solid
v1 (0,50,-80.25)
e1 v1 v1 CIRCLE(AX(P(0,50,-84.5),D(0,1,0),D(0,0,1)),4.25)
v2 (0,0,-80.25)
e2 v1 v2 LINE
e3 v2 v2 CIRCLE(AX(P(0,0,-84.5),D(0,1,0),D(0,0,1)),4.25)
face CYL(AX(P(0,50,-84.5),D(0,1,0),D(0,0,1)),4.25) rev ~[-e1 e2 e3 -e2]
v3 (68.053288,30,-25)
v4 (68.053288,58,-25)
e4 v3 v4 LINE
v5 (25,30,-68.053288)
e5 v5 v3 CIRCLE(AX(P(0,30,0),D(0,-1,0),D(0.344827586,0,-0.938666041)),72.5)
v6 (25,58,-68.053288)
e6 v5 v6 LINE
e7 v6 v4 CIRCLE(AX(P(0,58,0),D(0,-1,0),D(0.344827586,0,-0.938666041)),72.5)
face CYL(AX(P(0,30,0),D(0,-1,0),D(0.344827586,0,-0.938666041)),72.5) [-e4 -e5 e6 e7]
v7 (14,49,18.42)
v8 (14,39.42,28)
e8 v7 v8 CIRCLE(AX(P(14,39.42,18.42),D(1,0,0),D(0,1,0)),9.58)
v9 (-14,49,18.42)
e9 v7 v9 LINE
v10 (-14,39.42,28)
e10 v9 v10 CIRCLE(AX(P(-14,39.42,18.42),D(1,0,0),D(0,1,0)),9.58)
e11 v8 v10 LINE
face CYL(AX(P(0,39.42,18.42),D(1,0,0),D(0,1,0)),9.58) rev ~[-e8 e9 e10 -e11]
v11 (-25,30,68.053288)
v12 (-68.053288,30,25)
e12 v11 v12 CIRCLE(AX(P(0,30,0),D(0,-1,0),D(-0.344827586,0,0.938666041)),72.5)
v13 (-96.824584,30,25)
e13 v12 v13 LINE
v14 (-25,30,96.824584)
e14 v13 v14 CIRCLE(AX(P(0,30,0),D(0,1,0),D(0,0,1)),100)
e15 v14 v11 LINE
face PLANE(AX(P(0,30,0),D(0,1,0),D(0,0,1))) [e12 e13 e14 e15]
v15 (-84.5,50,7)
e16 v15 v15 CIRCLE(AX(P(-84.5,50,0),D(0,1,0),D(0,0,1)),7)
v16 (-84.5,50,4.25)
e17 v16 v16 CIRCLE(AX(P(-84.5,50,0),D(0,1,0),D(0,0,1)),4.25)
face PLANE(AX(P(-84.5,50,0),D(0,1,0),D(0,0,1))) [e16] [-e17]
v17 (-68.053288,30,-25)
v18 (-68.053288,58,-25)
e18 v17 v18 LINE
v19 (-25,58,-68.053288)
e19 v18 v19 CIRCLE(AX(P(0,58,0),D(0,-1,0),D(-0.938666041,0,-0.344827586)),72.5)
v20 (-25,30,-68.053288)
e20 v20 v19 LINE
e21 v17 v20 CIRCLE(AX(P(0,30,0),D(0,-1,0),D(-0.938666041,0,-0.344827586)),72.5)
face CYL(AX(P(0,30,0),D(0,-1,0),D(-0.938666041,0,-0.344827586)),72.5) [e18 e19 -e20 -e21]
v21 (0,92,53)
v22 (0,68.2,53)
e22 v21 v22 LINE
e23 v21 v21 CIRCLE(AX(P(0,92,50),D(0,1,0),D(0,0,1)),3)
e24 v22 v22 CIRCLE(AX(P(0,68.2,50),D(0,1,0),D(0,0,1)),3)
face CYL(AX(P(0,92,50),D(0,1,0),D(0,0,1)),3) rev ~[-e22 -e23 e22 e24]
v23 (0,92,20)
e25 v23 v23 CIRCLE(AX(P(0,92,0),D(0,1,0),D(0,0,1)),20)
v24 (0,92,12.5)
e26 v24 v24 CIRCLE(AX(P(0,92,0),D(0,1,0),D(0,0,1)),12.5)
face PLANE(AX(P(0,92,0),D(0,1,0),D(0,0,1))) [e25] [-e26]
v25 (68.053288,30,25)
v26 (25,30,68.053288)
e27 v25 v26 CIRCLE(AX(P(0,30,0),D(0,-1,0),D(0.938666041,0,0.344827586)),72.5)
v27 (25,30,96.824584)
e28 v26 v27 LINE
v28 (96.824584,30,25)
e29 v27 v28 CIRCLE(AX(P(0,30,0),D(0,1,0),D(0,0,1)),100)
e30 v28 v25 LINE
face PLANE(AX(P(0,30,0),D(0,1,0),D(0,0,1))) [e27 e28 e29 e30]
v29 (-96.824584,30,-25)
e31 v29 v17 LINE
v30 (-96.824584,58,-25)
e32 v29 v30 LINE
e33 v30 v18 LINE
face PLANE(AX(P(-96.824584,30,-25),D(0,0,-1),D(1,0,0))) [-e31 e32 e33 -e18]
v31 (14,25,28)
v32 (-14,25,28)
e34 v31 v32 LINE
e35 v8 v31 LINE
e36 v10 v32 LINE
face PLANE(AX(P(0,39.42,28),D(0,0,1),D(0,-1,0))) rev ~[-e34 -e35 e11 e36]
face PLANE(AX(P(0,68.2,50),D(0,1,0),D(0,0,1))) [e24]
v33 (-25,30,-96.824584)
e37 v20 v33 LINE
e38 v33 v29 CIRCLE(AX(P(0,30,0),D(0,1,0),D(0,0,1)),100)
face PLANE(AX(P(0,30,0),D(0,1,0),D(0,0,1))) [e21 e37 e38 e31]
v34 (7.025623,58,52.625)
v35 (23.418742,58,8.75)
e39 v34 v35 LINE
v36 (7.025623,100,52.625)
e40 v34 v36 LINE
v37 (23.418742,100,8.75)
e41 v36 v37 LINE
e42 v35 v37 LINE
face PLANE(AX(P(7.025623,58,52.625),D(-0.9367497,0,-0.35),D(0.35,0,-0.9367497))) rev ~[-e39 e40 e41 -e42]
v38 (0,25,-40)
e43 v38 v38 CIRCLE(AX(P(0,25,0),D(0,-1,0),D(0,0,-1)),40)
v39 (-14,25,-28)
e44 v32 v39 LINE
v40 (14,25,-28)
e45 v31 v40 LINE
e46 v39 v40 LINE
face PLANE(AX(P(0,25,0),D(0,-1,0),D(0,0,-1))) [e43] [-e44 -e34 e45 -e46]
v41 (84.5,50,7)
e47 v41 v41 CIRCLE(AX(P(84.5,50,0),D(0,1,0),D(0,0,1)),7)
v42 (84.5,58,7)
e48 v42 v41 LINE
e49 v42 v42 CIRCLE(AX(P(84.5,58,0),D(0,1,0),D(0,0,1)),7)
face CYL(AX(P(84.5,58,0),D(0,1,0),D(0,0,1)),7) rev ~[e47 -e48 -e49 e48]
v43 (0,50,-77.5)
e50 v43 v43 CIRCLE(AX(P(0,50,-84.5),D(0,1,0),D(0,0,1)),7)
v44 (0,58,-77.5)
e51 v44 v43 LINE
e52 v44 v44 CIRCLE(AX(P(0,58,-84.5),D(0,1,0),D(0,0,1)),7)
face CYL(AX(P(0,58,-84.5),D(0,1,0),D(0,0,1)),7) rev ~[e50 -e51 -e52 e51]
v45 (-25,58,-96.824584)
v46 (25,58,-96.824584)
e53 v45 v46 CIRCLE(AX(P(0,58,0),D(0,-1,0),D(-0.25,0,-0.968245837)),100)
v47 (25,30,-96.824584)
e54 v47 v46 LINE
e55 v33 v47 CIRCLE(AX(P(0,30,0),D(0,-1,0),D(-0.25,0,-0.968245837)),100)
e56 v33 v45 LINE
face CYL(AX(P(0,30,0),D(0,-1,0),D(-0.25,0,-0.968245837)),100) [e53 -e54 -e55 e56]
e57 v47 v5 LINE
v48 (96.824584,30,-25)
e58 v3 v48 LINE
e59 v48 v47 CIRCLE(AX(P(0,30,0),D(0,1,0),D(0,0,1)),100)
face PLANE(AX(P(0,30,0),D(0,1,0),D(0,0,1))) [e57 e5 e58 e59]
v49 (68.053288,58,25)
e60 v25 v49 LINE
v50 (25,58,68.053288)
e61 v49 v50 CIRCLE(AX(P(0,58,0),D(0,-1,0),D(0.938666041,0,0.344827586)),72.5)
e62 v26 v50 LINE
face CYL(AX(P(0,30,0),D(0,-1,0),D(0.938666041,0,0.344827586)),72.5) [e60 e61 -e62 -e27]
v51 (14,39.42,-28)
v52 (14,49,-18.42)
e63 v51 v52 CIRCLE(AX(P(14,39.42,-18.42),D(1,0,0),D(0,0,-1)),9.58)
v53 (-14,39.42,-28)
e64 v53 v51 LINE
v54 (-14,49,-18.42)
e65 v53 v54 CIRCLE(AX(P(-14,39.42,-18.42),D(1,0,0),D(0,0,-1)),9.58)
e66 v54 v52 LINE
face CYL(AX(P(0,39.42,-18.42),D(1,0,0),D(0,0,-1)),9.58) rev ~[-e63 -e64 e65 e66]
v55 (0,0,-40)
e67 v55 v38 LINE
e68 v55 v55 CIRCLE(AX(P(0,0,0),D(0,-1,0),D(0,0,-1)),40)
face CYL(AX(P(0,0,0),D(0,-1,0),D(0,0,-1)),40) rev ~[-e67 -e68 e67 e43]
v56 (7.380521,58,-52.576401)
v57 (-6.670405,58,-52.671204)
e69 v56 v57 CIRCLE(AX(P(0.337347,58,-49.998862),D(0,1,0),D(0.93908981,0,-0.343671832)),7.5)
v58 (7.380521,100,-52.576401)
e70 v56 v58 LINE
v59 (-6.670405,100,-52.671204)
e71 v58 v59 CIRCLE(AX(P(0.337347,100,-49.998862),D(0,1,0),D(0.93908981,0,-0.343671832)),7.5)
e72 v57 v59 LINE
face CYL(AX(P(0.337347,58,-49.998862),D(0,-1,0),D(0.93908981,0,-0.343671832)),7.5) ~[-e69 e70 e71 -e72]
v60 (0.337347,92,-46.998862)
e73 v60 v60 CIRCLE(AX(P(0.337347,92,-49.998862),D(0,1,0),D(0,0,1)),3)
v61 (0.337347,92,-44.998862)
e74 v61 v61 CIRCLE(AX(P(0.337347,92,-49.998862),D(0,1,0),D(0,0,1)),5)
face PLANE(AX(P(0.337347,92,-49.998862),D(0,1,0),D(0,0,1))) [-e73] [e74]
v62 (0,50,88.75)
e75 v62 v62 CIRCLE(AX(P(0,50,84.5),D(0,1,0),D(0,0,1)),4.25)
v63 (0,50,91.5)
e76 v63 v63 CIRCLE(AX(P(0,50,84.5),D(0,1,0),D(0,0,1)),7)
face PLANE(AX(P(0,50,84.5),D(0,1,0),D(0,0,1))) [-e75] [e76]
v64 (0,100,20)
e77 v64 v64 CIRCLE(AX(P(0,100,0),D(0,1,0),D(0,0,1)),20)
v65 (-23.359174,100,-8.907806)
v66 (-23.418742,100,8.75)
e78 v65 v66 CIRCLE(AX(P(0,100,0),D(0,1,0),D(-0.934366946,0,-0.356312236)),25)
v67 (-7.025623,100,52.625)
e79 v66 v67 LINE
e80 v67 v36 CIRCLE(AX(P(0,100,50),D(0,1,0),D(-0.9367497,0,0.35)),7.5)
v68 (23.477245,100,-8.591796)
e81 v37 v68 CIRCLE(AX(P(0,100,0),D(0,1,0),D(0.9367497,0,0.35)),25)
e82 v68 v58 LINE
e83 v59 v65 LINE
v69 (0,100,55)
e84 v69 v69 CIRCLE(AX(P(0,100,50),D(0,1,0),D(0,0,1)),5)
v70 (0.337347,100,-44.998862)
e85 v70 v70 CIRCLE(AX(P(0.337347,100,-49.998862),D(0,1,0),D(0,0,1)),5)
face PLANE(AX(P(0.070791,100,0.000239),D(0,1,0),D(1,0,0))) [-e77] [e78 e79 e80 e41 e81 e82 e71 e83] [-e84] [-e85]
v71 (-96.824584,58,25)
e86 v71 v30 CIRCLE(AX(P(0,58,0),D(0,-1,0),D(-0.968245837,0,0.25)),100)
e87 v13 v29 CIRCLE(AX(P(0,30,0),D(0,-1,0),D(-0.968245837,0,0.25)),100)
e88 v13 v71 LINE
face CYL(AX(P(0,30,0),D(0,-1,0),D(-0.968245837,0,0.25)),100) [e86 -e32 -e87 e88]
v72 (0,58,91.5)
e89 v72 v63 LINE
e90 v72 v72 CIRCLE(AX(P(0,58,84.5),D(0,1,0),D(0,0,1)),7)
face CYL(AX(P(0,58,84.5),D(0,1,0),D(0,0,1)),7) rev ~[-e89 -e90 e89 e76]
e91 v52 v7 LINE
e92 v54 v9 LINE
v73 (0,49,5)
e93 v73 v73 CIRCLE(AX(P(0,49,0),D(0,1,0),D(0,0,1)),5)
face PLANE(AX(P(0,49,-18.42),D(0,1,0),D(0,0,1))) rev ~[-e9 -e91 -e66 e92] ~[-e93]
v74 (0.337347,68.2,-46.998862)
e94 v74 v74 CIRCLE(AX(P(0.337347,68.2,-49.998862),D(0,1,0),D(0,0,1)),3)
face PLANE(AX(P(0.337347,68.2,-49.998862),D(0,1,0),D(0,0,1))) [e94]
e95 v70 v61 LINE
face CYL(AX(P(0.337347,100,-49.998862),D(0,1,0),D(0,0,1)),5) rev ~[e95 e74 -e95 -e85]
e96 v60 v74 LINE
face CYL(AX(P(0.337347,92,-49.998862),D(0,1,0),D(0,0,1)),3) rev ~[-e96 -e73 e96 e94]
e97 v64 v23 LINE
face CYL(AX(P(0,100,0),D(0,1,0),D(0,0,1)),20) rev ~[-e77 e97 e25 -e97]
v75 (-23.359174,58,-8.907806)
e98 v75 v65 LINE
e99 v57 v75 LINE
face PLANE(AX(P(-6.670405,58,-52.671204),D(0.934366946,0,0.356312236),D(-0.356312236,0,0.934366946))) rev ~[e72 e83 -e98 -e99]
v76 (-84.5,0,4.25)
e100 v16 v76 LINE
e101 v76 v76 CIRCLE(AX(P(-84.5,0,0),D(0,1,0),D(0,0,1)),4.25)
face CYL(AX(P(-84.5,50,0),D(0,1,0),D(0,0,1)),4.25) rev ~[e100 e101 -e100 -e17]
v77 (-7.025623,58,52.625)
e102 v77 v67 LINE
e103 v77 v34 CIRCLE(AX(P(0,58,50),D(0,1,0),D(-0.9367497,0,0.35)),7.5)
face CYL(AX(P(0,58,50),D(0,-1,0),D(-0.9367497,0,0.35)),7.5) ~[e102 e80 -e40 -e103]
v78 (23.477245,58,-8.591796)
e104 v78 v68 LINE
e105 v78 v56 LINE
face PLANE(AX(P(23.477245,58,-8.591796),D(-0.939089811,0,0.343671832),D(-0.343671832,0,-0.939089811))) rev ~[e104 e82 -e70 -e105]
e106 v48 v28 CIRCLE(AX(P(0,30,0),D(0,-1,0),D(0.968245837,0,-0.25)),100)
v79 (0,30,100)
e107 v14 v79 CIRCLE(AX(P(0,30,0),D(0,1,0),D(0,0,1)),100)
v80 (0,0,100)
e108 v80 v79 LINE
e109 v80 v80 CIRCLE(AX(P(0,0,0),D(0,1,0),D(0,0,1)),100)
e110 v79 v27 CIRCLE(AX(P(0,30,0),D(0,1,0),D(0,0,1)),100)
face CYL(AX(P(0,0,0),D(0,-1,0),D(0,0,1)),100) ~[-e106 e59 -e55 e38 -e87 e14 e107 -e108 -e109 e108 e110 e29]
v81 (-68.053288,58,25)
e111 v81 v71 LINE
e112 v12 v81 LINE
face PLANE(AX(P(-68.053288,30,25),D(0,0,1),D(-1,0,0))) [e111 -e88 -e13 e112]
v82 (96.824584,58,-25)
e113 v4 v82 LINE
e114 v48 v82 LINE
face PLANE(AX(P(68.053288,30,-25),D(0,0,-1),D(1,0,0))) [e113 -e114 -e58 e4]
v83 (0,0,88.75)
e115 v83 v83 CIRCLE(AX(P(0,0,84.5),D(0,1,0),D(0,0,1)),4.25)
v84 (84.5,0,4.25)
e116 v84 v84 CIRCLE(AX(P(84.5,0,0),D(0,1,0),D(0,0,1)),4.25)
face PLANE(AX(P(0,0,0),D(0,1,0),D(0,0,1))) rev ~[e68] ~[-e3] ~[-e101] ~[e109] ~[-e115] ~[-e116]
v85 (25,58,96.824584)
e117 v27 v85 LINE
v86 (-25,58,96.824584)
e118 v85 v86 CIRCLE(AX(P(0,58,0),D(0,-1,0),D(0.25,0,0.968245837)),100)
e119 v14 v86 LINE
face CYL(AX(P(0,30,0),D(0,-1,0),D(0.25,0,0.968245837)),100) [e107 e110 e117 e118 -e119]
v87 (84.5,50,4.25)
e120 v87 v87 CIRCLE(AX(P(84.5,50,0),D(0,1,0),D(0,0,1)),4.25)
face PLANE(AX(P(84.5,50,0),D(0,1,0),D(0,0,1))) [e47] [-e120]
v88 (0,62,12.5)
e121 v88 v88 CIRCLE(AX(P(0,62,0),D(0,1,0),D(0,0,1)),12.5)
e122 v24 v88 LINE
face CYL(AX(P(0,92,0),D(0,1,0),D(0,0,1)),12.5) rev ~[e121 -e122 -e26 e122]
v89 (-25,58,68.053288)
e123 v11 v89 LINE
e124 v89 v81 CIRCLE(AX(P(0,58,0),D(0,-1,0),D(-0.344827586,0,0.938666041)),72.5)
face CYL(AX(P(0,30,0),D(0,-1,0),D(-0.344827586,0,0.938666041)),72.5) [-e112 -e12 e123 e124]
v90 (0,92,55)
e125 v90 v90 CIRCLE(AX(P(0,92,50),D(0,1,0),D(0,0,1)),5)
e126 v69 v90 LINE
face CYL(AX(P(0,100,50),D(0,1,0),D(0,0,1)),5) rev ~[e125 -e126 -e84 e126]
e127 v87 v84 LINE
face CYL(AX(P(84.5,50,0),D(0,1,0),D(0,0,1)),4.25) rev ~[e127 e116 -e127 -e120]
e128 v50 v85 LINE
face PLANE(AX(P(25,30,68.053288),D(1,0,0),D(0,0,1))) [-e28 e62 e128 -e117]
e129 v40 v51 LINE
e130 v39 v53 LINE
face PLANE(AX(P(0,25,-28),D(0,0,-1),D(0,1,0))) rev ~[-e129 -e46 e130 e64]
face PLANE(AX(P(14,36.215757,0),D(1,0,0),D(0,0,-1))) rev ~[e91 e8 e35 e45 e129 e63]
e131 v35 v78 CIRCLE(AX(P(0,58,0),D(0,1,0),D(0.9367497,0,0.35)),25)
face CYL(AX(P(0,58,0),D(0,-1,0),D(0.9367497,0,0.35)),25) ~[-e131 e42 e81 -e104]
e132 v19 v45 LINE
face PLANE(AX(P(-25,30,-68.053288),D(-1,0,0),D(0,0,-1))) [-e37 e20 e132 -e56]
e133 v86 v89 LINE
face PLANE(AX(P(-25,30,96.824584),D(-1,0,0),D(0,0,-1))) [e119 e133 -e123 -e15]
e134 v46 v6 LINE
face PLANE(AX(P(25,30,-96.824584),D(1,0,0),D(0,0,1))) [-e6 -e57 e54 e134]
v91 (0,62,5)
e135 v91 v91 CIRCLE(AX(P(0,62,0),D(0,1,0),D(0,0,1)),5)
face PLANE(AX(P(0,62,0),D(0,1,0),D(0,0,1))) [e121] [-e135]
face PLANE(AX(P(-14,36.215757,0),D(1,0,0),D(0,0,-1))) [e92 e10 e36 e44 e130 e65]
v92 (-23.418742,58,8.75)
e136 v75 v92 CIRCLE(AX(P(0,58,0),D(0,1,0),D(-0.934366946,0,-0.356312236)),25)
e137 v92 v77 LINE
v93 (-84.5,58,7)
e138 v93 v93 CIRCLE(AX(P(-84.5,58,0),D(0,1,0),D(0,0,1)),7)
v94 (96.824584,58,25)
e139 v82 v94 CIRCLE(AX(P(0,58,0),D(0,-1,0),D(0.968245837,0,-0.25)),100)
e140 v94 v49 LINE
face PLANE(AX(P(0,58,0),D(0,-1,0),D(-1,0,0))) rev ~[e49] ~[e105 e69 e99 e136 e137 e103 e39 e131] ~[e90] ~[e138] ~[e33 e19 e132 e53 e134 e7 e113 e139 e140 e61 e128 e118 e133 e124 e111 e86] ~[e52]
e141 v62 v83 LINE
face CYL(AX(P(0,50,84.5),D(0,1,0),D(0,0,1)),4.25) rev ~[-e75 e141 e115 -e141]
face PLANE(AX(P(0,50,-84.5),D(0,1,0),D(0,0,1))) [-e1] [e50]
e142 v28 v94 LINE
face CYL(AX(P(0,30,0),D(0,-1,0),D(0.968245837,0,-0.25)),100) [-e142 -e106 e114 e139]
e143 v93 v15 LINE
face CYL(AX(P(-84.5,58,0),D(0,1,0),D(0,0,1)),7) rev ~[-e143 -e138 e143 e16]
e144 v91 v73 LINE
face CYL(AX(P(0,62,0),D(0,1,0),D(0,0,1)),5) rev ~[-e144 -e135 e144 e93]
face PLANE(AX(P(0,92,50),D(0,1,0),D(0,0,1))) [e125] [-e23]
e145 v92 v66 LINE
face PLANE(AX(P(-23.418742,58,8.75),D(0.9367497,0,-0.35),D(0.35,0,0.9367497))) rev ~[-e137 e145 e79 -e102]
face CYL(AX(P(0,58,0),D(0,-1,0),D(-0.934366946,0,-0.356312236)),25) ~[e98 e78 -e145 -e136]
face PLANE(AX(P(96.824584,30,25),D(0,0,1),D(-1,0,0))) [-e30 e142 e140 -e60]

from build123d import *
from build123d.topology import SkipClean

# Parameters (mm, degrees)
BASE_FLANGE_SKETCH_R               = 100
BASE_FLANGE_200_DEPTH              = 30
MOUNTING_PAD_DEPTH                 = 28
MOUNTING_COUNTERBORES_SKETCH_R     = 7
MOUNTING_COUNTERBORES_4X_14_DEPTH  = 8
MOUNTING_HOLES_SKETCH_R            = 4.25
MOUNTING_HOLES_4X_8_5_DEPTH        = 50
SUPPORT_BOSS_DEPTH                 = 42
BEARING_COUNTERBORE_SKETCH_R       = 20
BEARING_COUNTERBORE_40_DEPTH       = 8
BEARING_BORE_SKETCH_R              = 12.5
BEARING_BORE_25_DEPTH              = 30
THROUGH_BORE_SKETCH_R              = 5
THROUGH_BORE_10_DEPTH              = 13
UNDERSIDE_RECESS_SKETCH_R          = 40
UNDERSIDE_RECESS_80_DEPTH          = 25
SIDE_SLOT_DEPTH                    = 14
BOSS_HOLE_COUNTERBORES_SKETCH_R    = 5
BOSS_HOLE_COUNTERBORES_2X_10_DEPTH = 8
BOSS_PIN_HOLES_SKETCH_R            = 3
BOSS_PIN_HOLES_2X_6_DEPTH          = 23.8


with BuildPart() as part:
    # Base Flange Sketch → Base Flange Ø200 (new body)
    with BuildSketch(Plane(origin=(0, 0, 0), x_dir=(1, 0, 0), z_dir=(0, 1, 0))):
        with Locations(Location((0, 0, 0), (0, 0, 270))):
            Circle(BASE_FLANGE_SKETCH_R)
    extrude(amount=BASE_FLANGE_200_DEPTH)

    # Mounting Pad Sketch → Mounting Pad (add)
    with SkipClean():  # the faces are left unmerged after this step: merging them gives an invalid solid
        with BuildSketch(Plane(origin=(0, 30, 0), x_dir=(1, 0, 0), z_dir=(0, 1, 0))):
            with BuildLine():
                Line((68.053287944, 25), (96.824583655, 25))
                ThreePointArc((96.824583655, 25), (100, 0), (96.824583655, -25))
                Line((96.824583655, -25), (68.053287944, -25))
                ThreePointArc((68.053287944, -25), (51.265241636, -51.265241636), (25, -68.053287944))
                Line((25, -68.053287944), (25, -96.824583655))
                ThreePointArc((25, -96.824583655), (0, -100), (-25, -96.824583655))
                Line((-25, -96.824583655), (-25, -68.053287944))
                ThreePointArc((-25, -68.053287944), (-51.265241636, -51.265241636), (-68.053287944, -25))
                Line((-68.053287944, -25), (-96.824583655, -25))
                ThreePointArc((-96.824583655, -25), (-100, 0), (-96.824583655, 25))
                Line((-96.824583655, 25), (-68.053287944, 25))
                ThreePointArc((-68.053287944, 25), (-51.265241636, 51.265241636), (-25, 68.053287944))
                Line((-25, 68.053287944), (-25, 96.824583655))
                ThreePointArc((-25, 96.824583655), (0, 100), (25, 96.824583655))
                Line((25, 96.824583655), (25, 68.053287944))
                ThreePointArc((25, 68.053287944), (51.265241636, 51.265241636), (68.053287944, 25))
            make_face()
        extrude(amount=MOUNTING_PAD_DEPTH)

    # Mounting Counterbores Sketch → Mounting Counterbores 4xØ14 (cut)
    with SkipClean():  # the faces are left unmerged after this step: merging them gives an invalid solid
        with BuildSketch(Plane(origin=(0, 58, 0), x_dir=(1, 0, 0), z_dir=(0, 1, 0))):
            with Locations(Location((0, 84.5, 0), (0, 0, 270))):
                Circle(MOUNTING_COUNTERBORES_SKETCH_R)
            with Locations(Location((84.5, 0, 0), (0, 0, 270))):
                Circle(MOUNTING_COUNTERBORES_SKETCH_R)
            with Locations(Location((0, -84.5, 0), (0, 0, 270))):
                Circle(MOUNTING_COUNTERBORES_SKETCH_R)
            with Locations(Location((-84.5, 0, 0), (0, 0, 270))):
                Circle(MOUNTING_COUNTERBORES_SKETCH_R)
        extrude(amount=-MOUNTING_COUNTERBORES_4X_14_DEPTH, mode=Mode.SUBTRACT)

    # Mounting Holes Sketch → Mounting Holes 4xØ8.5 (cut)
    with SkipClean():  # the faces are left unmerged after this step: merging them gives an invalid solid
        with BuildSketch(Plane(origin=(0, 50, 0), x_dir=(1, 0, 0), z_dir=(0, 1, 0))):
            with Locations(Location((0, 84.5, 0), (0, 0, 270))):
                Circle(MOUNTING_HOLES_SKETCH_R)
            with Locations(Location((84.5, 0, 0), (0, 0, 270))):
                Circle(MOUNTING_HOLES_SKETCH_R)
            with Locations(Location((0, -84.5, 0), (0, 0, 270))):
                Circle(MOUNTING_HOLES_SKETCH_R)
            with Locations(Location((-84.5, 0, 0), (0, 0, 270))):
                Circle(MOUNTING_HOLES_SKETCH_R)
        extrude(amount=-MOUNTING_HOLES_4X_8_5_DEPTH, mode=Mode.SUBTRACT)

    # Support Boss Sketch → Support Boss (add)
    with SkipClean():  # the faces are left unmerged after this step: merging them gives an invalid solid
        with BuildSketch(Plane(origin=(0, 58, 0), x_dir=(1, 0, 0), z_dir=(0, 1, 0))):
            with BuildLine():
                Line((-6.670404666, 52.671203723), (-23.359173661, 8.907805895))
                ThreePointArc((-23.359173661, 8.907805895), (-24.999857744, 0.084337338), (-23.418742494, -8.75))
                Line((-23.418742494, -8.75), (-7.025622749, -52.625))
                ThreePointArc((-7.025622749, -52.625), (-1e-09, -57.5), (7.025622747, -52.625))
                Line((7.025622747, -52.625), (23.418742494, -8.75))
                ThreePointArc((23.418742494, -8.75), (24.999857744, -0.084337338), (23.477245263, 8.591795789))
                Line((23.477245263, 8.591795789), (7.380521011, 52.576400691))
                ThreePointArc((7.380521011, 52.576400691), (0.387949547, 57.498691247), (-6.670404666, 52.671203723))
            make_face()
        extrude(amount=SUPPORT_BOSS_DEPTH)

    # Bearing Counterbore Sketch → Bearing Counterbore Ø40 (cut)
    with SkipClean():  # the faces are left unmerged after this step: merging them gives an invalid solid
        with BuildSketch(Plane(origin=(0, 100, 0), x_dir=(1, 0, 0), z_dir=(0, 1, 0))):
            with Locations(Location((0, 0, 0), (0, 0, 270))):
                Circle(BEARING_COUNTERBORE_SKETCH_R)
        extrude(amount=-BEARING_COUNTERBORE_40_DEPTH, mode=Mode.SUBTRACT)

    # Bearing Bore Sketch → Bearing Bore Ø25 (cut)
    with SkipClean():  # the faces are left unmerged after this step: merging them gives an invalid solid
        with BuildSketch(Plane(origin=(0, 92, 0), x_dir=(1, 0, 0), z_dir=(0, 1, 0))):
            with Locations(Location((0, 0, 0), (0, 0, 270))):
                Circle(BEARING_BORE_SKETCH_R)
        extrude(amount=-BEARING_BORE_25_DEPTH, mode=Mode.SUBTRACT)

    # Through Bore Sketch → Through Bore Ø10 (cut)
    with SkipClean():  # the faces are left unmerged after this step: merging them gives an invalid solid
        with BuildSketch(Plane(origin=(0, 62, 0), x_dir=(1, 0, 0), z_dir=(0, 1, 0))):
            with Locations(Location((0, 0, 0), (0, 0, 270))):
                Circle(THROUGH_BORE_SKETCH_R)
        extrude(amount=-THROUGH_BORE_10_DEPTH, mode=Mode.SUBTRACT)

    # Underside Recess Sketch → Underside Recess Ø80 (cut)
    with SkipClean():  # the faces are left unmerged after this step: merging them gives an invalid solid
        with BuildSketch(Plane.XZ):
            with Locations(Location((0, 0, 0), (0, 0, 270))):
                Circle(UNDERSIDE_RECESS_SKETCH_R)
        extrude(amount=-UNDERSIDE_RECESS_80_DEPTH, mode=Mode.SUBTRACT)

    # Side Slot Sketch → Side Slot (cut, symmetric)
    with SkipClean():  # the faces are left unmerged after this step: merging them gives an invalid solid
        with BuildSketch(Plane(origin=(0, 0, 0), x_dir=(0, 0, -1), z_dir=(1, 0, 0))):
            with BuildLine():
                Line((-28, 25), (28, 25))
                Line((28, 25), (28, 39.42))
                ThreePointArc((28, 39.42), (25.194082964, 46.194082964), (18.42, 49))
                Line((18.42, 49), (-18.42, 49))
                ThreePointArc((-18.42, 49), (-25.194082964, 46.194082964), (-28, 39.42))
                Line((-28, 39.42), (-28, 25))
            make_face()
        extrude(amount=SIDE_SLOT_DEPTH, both=True, mode=Mode.SUBTRACT)

    # Boss Hole Counterbores Sketch → Boss Hole Counterbores 2xØ10 (cut)
    with SkipClean():  # the faces are left unmerged after this step: merging them gives an invalid solid
        with BuildSketch(Plane(origin=(0, 100, 0), x_dir=(1, 0, 0), z_dir=(0, 1, 0))):
            with Locations(Location((0.337347432, 49.998861954, 0), (0, 0, 270))):
                Circle(BOSS_HOLE_COUNTERBORES_SKETCH_R)
            with Locations(Location((-1e-09, -50, 0), (0, 0, 270))):
                Circle(BOSS_HOLE_COUNTERBORES_SKETCH_R)
        extrude(amount=-BOSS_HOLE_COUNTERBORES_2X_10_DEPTH, mode=Mode.SUBTRACT)

    # Boss Pin Holes Sketch → Boss Pin Holes 2xØ6 (cut)
    with SkipClean():  # the faces are left unmerged after this step: merging them gives an invalid solid
        with BuildSketch(Plane(origin=(0, 92, 0), x_dir=(1, 0, 0), z_dir=(0, 1, 0))):
            with Locations(Location((0.337347432, 49.998861954, 0), (0, 0, 270))):
                Circle(BOSS_PIN_HOLES_SKETCH_R)
            with Locations(Location((-1e-09, -50, 0), (0, 0, 270))):
                Circle(BOSS_PIN_HOLES_SKETCH_R)
        extrude(amount=-BOSS_PIN_HOLES_2X_6_DEPTH, mode=Mode.SUBTRACT)


solid = part.part
